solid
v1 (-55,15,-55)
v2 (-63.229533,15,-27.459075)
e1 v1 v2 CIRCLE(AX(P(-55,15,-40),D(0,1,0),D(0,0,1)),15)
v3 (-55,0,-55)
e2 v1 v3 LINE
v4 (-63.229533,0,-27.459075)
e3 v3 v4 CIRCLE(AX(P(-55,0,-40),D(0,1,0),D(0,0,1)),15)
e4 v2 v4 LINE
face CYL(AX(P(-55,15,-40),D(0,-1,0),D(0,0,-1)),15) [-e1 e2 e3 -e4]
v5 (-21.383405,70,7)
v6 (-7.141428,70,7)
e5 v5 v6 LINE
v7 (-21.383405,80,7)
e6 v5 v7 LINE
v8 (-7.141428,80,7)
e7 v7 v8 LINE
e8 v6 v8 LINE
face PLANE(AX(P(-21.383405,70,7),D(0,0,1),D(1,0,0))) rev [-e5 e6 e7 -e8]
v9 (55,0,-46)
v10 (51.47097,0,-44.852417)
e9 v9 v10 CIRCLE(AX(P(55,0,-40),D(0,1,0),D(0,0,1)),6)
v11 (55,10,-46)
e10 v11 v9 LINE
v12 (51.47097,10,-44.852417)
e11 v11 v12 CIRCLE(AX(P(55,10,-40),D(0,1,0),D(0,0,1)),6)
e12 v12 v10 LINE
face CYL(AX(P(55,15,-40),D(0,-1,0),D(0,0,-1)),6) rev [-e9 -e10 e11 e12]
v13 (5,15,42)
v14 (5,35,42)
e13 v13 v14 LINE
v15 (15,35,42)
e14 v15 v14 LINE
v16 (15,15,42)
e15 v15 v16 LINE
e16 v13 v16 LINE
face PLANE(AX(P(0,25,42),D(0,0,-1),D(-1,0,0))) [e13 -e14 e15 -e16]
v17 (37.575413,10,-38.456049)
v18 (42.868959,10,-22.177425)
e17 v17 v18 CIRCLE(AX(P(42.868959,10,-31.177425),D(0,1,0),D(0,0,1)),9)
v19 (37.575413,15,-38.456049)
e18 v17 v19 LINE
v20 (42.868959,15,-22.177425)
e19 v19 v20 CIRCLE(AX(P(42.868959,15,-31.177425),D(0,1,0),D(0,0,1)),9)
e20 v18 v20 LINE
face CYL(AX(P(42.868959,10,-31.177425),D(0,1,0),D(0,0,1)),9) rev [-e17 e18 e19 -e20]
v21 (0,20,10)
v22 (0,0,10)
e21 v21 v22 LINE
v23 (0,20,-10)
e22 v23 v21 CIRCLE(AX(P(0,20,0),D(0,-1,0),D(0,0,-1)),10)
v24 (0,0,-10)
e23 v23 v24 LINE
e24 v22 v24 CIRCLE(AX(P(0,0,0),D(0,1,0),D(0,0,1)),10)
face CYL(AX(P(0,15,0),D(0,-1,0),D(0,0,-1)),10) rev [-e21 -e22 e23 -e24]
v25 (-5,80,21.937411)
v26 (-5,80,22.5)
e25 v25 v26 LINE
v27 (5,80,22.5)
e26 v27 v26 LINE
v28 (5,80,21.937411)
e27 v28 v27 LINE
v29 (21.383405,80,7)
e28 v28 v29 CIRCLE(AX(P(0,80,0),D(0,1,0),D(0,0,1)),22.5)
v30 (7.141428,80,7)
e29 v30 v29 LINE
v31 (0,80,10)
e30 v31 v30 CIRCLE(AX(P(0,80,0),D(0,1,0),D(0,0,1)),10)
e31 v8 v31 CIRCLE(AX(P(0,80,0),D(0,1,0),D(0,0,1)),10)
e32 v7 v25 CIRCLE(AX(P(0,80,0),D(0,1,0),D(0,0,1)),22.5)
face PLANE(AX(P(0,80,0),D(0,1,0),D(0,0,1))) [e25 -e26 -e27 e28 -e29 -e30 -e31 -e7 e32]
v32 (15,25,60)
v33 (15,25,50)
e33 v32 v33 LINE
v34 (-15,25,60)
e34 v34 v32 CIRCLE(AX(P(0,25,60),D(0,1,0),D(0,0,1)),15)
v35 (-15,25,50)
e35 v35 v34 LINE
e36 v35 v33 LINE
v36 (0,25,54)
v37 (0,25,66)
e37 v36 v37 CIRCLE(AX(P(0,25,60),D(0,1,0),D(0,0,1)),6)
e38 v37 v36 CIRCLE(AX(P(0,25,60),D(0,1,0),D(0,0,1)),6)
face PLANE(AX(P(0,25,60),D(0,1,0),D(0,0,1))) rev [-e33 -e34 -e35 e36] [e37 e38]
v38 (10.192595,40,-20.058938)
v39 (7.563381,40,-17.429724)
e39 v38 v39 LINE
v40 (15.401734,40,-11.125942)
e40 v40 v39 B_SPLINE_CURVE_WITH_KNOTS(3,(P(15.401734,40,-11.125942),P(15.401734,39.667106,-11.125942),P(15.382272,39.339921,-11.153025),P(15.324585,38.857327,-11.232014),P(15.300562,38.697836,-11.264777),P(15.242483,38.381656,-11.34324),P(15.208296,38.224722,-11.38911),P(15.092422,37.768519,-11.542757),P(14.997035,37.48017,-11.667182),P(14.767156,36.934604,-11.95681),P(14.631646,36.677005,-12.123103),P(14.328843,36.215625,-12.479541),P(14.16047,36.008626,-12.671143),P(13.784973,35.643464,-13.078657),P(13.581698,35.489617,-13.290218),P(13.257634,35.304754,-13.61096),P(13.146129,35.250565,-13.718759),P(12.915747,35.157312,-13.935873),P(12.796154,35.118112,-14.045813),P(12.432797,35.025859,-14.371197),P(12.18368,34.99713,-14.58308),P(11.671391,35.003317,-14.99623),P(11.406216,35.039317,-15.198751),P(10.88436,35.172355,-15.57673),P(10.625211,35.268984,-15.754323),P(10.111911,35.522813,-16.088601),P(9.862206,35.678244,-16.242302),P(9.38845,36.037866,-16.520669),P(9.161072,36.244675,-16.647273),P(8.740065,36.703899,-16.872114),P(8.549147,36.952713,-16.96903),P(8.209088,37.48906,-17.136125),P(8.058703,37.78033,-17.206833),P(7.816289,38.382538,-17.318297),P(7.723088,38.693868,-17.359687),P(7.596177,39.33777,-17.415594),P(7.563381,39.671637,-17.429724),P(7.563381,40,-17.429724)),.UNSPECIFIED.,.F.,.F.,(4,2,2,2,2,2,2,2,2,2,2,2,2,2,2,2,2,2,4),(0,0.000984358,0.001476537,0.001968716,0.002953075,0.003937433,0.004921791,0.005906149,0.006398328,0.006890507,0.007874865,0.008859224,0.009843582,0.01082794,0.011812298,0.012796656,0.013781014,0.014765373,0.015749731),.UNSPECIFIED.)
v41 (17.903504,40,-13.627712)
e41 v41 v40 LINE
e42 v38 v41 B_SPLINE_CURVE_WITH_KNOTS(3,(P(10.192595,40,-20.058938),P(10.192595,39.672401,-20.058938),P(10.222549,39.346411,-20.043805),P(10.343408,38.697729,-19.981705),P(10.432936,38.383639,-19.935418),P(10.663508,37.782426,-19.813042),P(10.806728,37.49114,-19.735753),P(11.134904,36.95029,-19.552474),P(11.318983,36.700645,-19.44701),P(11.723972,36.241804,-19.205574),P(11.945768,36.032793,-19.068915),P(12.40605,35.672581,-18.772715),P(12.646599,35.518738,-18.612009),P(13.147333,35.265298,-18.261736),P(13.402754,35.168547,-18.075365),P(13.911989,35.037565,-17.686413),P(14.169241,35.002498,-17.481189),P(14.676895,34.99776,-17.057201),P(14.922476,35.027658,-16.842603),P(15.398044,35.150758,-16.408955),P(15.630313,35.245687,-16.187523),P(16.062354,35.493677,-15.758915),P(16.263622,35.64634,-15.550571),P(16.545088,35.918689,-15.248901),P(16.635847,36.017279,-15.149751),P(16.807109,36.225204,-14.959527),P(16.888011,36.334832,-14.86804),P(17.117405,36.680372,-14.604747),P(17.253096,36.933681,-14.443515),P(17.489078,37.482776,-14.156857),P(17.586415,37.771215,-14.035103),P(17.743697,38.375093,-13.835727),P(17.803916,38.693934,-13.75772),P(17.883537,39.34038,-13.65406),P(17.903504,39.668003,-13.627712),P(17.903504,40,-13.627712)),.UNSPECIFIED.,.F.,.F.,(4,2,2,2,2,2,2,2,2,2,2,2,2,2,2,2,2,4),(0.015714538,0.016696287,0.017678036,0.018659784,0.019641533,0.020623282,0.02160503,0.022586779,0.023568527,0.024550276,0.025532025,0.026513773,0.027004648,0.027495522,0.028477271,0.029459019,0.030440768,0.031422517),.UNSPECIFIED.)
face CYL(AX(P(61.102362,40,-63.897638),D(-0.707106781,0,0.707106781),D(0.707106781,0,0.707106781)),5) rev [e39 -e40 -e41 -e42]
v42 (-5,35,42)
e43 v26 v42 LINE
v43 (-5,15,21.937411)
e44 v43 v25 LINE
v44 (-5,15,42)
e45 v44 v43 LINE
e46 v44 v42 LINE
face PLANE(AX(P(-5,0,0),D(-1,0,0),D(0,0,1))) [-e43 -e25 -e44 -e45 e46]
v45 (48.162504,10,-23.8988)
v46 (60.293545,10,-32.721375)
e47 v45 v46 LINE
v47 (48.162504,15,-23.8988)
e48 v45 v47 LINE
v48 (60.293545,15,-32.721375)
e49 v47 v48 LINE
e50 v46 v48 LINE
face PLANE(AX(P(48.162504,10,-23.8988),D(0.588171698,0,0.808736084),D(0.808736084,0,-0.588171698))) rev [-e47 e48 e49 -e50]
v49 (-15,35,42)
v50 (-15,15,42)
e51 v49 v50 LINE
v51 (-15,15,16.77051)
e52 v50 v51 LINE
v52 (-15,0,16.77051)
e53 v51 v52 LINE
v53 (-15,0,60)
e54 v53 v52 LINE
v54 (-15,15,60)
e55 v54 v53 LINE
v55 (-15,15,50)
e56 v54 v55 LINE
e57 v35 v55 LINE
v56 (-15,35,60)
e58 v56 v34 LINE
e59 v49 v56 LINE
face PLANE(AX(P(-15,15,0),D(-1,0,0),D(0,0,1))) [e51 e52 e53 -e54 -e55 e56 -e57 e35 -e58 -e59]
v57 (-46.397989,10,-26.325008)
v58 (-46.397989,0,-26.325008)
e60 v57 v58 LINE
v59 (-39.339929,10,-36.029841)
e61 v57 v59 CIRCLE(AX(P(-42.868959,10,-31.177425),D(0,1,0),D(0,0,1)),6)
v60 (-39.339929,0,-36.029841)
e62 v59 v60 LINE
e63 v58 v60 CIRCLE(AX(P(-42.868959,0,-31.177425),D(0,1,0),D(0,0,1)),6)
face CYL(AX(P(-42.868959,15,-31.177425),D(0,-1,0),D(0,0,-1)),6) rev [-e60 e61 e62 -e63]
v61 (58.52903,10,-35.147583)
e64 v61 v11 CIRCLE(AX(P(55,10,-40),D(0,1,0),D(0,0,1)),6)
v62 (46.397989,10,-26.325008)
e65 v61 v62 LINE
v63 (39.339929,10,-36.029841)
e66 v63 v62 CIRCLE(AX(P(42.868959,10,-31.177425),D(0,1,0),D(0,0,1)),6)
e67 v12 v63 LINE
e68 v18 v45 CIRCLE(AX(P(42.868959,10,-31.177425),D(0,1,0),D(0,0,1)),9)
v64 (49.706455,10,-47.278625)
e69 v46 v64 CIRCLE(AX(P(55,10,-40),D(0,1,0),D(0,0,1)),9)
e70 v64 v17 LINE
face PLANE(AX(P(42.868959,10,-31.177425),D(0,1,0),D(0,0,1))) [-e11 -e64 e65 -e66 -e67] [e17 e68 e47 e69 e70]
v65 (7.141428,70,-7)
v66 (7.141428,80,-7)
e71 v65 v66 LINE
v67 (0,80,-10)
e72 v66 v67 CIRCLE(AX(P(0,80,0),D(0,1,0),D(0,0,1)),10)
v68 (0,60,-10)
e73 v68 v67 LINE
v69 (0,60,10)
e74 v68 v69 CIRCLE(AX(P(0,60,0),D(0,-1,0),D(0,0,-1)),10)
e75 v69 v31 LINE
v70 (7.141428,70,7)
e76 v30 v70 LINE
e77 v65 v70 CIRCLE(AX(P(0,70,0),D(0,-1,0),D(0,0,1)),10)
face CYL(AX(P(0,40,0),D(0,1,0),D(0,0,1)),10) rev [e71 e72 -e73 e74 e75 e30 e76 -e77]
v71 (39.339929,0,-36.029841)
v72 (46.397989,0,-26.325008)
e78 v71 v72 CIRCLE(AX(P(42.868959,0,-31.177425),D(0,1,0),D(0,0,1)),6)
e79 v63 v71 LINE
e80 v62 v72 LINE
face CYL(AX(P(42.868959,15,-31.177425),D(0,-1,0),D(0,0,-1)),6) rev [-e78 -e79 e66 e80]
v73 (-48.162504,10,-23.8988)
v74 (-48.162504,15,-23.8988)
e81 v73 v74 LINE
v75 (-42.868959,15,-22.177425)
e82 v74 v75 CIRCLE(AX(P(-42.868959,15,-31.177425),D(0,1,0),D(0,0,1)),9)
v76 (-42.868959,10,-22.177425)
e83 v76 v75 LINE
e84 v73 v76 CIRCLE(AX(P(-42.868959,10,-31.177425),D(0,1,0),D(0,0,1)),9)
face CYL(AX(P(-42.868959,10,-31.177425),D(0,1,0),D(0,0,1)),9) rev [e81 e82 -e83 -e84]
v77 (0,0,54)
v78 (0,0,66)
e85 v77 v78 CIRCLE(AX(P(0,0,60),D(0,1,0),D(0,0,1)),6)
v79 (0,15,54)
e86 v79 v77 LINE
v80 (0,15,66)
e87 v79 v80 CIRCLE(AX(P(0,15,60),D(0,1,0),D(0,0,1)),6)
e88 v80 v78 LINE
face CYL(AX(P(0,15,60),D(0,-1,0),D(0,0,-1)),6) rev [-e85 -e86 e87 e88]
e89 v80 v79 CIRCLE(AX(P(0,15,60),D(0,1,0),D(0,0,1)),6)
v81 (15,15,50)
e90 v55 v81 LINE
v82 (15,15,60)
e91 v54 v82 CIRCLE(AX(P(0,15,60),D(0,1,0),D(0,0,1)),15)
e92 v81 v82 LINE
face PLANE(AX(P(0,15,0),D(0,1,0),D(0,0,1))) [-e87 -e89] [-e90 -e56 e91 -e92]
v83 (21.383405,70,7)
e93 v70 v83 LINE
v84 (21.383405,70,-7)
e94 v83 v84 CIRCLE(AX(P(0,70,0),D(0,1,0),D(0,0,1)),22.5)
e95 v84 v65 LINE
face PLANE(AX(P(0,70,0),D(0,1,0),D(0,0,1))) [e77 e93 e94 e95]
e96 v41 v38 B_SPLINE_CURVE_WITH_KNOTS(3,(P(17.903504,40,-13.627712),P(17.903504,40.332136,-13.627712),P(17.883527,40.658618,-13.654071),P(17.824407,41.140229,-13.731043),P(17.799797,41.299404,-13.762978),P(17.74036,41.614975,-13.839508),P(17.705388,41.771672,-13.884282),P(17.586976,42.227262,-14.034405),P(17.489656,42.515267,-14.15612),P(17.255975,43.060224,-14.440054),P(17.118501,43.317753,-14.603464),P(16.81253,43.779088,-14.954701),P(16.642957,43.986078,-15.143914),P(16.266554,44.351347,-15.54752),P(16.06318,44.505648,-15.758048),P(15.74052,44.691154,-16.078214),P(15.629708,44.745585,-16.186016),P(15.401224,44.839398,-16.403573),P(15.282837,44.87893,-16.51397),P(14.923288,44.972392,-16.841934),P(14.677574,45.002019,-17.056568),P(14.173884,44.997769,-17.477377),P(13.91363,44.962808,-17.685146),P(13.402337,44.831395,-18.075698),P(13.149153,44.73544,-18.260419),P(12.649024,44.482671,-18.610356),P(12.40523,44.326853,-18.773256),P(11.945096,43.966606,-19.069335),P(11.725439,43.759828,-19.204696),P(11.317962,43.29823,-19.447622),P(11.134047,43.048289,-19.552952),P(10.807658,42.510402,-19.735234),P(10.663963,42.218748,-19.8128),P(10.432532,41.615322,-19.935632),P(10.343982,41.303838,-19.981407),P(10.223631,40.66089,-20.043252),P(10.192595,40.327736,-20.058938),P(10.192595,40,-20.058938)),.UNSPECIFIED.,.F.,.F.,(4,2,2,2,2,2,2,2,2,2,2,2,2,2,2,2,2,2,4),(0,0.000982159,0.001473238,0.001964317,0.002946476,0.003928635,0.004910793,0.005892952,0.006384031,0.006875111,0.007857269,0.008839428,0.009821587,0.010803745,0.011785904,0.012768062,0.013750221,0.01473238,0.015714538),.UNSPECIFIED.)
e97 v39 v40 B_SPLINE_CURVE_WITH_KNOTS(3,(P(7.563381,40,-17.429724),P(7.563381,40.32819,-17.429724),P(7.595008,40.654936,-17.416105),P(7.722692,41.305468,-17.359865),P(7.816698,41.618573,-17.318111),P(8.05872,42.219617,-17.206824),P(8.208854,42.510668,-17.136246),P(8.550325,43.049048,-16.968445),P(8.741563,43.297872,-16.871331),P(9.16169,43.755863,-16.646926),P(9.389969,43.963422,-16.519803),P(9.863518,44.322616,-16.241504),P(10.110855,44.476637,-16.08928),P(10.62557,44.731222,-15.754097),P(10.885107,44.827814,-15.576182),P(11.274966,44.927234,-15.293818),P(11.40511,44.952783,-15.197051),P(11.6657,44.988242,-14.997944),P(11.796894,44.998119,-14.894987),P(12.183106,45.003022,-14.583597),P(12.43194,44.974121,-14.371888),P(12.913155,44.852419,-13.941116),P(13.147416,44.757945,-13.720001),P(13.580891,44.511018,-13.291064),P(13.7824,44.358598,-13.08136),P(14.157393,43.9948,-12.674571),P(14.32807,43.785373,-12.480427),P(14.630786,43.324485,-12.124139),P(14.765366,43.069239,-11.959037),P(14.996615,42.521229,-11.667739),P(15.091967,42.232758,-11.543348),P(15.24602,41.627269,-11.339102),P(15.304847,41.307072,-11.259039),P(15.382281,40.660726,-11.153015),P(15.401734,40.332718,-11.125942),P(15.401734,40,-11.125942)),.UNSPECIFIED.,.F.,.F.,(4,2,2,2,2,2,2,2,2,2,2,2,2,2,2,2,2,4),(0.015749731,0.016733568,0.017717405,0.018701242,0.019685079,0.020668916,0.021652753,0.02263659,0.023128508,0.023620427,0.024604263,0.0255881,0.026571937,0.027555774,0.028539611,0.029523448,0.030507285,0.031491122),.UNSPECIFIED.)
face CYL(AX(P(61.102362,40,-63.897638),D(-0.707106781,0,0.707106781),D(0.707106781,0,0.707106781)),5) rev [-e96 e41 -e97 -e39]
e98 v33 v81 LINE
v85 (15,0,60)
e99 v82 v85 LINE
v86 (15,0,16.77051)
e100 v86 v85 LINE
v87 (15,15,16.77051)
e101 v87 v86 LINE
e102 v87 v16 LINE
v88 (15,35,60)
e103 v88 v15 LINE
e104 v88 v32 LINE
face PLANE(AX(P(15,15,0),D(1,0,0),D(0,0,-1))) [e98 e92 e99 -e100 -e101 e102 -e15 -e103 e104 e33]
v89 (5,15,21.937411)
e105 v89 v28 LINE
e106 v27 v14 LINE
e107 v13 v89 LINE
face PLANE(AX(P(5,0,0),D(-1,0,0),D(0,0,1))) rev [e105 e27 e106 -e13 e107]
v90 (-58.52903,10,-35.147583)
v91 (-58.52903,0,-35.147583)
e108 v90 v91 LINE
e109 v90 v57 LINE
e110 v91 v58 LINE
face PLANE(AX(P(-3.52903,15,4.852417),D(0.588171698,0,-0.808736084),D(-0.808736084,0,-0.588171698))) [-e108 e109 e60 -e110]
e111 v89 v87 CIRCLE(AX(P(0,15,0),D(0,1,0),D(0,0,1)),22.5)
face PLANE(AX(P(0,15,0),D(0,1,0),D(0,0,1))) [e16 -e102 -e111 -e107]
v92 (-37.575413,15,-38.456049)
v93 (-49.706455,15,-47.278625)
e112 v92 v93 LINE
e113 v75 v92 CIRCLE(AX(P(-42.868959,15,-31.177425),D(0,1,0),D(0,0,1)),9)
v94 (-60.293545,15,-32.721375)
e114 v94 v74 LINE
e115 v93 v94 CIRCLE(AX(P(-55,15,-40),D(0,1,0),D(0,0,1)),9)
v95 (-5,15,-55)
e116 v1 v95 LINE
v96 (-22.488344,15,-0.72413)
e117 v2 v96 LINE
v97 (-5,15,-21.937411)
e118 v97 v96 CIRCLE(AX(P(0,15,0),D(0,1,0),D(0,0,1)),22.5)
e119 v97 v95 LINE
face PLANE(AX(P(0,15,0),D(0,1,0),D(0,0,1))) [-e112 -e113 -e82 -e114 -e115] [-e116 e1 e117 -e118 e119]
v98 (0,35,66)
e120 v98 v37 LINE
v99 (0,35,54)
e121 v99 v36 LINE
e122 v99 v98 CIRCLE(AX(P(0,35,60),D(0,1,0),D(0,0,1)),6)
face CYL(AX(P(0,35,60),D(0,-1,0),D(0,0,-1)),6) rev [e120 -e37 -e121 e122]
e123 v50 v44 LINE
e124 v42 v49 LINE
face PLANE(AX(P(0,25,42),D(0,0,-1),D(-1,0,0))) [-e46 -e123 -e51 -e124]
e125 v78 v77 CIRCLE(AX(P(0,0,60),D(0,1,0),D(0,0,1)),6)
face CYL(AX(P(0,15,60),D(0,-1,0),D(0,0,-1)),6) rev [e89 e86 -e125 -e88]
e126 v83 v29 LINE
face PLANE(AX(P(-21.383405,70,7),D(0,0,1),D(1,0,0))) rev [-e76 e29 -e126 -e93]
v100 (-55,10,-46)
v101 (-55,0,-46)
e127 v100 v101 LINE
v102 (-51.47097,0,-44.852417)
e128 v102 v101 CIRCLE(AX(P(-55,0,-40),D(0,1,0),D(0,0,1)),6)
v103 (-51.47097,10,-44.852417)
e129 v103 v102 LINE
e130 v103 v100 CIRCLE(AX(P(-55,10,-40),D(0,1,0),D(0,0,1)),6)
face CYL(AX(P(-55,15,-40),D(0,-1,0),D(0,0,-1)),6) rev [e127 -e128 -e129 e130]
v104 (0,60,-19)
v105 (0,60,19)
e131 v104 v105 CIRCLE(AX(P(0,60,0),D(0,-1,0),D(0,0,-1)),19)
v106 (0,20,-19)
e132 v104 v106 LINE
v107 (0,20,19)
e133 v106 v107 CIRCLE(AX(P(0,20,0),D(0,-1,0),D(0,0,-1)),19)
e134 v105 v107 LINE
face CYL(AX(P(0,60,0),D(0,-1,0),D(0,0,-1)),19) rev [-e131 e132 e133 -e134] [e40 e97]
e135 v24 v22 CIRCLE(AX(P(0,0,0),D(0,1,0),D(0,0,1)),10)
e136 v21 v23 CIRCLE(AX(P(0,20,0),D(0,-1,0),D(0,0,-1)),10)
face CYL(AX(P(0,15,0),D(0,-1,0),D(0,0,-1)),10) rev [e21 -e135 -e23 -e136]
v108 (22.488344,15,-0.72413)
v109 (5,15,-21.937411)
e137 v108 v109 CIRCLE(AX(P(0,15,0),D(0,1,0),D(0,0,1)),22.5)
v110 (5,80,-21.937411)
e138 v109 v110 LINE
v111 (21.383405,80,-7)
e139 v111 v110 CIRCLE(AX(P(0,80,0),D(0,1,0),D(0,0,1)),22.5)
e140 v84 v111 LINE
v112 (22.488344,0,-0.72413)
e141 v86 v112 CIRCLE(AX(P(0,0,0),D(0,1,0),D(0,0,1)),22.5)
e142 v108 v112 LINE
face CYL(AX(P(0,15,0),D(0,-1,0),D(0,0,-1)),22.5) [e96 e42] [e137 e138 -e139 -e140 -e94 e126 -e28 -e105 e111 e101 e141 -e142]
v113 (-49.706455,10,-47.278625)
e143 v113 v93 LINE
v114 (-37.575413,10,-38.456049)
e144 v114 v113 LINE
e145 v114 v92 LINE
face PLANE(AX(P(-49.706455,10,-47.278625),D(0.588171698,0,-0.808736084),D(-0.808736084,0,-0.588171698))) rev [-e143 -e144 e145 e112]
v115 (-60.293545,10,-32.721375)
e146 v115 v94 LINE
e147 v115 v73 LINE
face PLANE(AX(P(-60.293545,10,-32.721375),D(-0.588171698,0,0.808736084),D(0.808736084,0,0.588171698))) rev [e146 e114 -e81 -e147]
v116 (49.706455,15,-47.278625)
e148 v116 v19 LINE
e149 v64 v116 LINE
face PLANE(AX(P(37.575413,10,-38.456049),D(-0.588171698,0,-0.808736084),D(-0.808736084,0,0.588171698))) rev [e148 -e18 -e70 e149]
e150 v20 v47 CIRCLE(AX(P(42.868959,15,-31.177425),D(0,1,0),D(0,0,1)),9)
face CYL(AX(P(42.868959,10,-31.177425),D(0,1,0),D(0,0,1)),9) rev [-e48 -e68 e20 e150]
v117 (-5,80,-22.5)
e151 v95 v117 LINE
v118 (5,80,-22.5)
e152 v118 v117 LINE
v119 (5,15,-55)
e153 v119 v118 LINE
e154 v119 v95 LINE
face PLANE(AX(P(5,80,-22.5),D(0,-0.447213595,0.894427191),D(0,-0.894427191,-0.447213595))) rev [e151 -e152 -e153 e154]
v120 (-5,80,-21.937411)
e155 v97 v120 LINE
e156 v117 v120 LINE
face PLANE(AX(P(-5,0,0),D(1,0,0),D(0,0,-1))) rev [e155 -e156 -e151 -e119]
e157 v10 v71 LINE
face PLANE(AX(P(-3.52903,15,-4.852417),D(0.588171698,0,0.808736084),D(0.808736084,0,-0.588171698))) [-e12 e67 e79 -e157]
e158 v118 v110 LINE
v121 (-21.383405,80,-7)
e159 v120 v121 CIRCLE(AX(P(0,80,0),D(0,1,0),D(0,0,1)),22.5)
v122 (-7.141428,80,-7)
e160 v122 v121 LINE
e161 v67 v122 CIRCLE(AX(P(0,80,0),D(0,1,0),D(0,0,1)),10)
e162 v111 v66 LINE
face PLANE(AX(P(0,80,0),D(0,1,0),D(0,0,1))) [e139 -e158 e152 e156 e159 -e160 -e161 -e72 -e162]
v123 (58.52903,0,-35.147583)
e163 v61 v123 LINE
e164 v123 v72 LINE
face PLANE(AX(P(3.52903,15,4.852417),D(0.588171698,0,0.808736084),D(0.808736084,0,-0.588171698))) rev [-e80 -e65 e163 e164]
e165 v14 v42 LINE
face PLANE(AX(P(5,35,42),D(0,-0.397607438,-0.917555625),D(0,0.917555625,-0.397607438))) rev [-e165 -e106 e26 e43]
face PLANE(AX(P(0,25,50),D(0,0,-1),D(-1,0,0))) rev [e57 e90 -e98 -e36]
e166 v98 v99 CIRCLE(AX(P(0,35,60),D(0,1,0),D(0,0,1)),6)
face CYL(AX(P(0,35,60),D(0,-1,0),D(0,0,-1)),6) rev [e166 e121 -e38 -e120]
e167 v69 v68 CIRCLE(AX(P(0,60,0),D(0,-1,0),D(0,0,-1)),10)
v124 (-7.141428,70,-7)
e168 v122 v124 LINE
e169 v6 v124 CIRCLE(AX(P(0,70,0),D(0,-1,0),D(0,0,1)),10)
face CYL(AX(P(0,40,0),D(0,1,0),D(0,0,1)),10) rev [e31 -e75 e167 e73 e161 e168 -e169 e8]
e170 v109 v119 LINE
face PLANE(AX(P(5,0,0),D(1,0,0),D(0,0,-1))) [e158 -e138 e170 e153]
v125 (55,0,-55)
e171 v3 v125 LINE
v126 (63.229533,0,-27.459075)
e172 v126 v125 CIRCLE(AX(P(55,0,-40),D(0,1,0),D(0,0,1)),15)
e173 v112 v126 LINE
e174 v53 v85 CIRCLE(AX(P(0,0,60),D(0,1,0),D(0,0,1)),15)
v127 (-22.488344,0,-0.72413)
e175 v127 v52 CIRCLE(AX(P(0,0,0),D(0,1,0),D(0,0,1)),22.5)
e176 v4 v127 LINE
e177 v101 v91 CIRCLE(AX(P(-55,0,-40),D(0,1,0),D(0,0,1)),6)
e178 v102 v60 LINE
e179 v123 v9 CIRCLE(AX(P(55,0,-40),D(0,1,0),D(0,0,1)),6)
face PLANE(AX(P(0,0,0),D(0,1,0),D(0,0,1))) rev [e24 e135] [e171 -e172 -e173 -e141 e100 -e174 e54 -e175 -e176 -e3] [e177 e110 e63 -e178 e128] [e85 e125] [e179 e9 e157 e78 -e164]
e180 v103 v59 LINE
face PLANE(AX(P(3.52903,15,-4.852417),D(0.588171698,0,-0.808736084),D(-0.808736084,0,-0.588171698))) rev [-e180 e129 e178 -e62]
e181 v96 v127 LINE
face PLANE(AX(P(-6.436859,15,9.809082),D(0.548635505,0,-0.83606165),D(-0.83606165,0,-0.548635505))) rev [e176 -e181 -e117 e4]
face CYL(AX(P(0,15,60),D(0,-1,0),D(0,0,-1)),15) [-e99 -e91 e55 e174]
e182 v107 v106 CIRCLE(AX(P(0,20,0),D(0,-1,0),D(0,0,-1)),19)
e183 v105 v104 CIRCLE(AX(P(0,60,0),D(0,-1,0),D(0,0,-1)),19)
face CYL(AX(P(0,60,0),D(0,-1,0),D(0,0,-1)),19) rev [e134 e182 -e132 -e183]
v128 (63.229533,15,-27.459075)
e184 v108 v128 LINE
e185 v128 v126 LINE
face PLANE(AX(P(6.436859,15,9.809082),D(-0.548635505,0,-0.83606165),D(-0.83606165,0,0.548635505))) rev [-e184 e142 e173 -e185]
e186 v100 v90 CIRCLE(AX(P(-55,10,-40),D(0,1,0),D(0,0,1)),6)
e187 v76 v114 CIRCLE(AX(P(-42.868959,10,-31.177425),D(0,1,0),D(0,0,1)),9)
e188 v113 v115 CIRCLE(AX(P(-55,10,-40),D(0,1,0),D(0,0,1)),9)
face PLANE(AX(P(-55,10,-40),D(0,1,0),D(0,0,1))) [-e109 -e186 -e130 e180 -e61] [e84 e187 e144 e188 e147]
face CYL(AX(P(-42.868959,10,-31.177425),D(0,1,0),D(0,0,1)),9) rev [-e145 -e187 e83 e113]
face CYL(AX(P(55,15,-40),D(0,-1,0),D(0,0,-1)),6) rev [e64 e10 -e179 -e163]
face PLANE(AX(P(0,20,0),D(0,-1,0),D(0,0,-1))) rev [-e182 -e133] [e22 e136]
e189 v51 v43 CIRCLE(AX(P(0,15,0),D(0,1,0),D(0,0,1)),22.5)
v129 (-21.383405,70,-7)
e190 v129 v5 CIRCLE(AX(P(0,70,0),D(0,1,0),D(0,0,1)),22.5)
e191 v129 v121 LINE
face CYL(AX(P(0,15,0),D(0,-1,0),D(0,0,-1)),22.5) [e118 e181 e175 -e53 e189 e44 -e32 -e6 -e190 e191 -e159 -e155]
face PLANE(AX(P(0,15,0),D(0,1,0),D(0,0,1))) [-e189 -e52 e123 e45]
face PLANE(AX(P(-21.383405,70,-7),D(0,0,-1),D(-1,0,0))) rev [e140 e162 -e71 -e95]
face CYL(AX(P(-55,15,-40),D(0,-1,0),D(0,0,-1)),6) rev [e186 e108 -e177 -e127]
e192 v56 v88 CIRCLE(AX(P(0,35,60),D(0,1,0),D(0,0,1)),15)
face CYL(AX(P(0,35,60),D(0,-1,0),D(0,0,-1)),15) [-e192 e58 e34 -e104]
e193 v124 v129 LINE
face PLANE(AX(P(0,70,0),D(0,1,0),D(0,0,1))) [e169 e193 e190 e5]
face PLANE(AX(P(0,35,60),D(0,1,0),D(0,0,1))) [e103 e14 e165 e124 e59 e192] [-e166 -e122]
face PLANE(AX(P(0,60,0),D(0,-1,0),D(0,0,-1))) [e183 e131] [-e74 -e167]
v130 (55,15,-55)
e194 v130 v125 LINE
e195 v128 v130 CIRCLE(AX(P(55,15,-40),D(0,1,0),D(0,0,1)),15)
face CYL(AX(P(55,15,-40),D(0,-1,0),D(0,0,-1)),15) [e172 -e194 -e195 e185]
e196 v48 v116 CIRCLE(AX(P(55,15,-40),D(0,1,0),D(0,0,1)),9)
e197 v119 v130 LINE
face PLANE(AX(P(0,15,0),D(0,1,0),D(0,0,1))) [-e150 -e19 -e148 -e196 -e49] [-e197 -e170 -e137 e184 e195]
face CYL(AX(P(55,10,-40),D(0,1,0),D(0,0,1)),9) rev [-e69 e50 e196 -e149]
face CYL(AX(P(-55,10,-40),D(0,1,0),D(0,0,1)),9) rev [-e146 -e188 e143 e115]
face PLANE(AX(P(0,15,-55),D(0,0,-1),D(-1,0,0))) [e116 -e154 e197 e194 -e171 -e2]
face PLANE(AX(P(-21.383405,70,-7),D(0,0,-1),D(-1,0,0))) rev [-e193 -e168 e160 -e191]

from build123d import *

# Parameters (mm, degrees)
TRI_ARM_BASE_PROFILE_R         = 22.5
TRI_ARM_BASE_PROFILE_R_2       = 10
TRI_ARM_BASE_PROFILE_R_3       = 6
TRI_ARM_BASE_PLATE_DEPTH       = 15
ARM_POCKET_DEPTH               = 5
CLEVIS_LUG_PROFILE_W           = 30
CLEVIS_LUG_PROFILE_H           = 8
CLEVIS_LUG_DEPTH               = 10
CLEVIS_LUG_EXTENSION_PROFILE_R = 6
CLEVIS_LUG_EXTENSION_DEPTH     = 10
TRUNNION_HUB_PROFILE_45_R      = 22.5
TRUNNION_HUB_45_DEPTH          = 65
HUB_ENTRY_BORE_PROFILE_20_R    = 10
HUB_ENTRY_BORE_20_DEPTH        = 5
HUB_BORE_PROFILE_38_R          = 19
HUB_BORE_38_DEPTH              = 40
HUB_START                      = -40
HUB_THROUGH_BORE_PROFILE_20_R  = 10
HUB_THROUGH_BORE_20_DEPTH      = 40
HUB_START_2                    = -10
HUB_TOP_SLOT_14MM_DEPTH        = 10
GUSSET_RIB_DEPTH               = 5
CLEVIS_PIN_HOLE_PROFILE_10_R   = 5
CLEVIS_PIN_HOLE_10_DEPTH       = 131.096118313


with BuildPart() as part:
    # Tri-Arm Base Profile → Tri-Arm Base Plate (new body)
    # profile 1 of 3: a face of its own
    with BuildSketch(Plane(origin=(0, 0, 0), x_dir=(1, 0, 0), z_dir=(0, 1, 0))):
        with BuildLine():
            Line((55, 55), (-55, 55))
            ThreePointArc((-55, 55), (-69.372088771, 44.294538898), (-63.22953257, 27.459075246))
            Line((-63.22953257, 27.459075246), (-22.488344437, 0.724130156))
            ThreePointArc((-22.488344437, 0.724130156), (0, 22.5), (22.488344437, 0.724130156))
            Line((22.488344437, 0.724130156), (63.22953257, 27.459075246))
            ThreePointArc((63.22953257, 27.459075246), (69.372088771, 44.294538898), (55, 55))
        make_face()
        with BuildLine():
            ThreePointArc((-58.529030186, 35.147583494), (-59.852416506, 43.529030186), (-51.470969814, 44.852416506))
            Line((-51.470969814, 44.852416506), (-39.339928549, 36.029841041))
            ThreePointArc((-39.339928549, 36.029841041), (-38.01654223, 27.648394349), (-46.397988922, 26.325008029))
            Line((-46.397988922, 26.325008029), (-58.529030186, 35.147583494))
        make_face(mode=Mode.SUBTRACT)
        with BuildLine():
            ThreePointArc((51.470969814, 44.852416506), (59.852416506, 43.529030186), (58.529030186, 35.147583494))
            Line((58.529030186, 35.147583494), (46.397988922, 26.325008029))
            ThreePointArc((46.397988922, 26.325008029), (38.01654223, 27.648394349), (39.339928549, 36.029841041))
            Line((39.339928549, 36.029841041), (51.470969814, 44.852416506))
        make_face(mode=Mode.SUBTRACT)
    # profile 2 of 3: a face of its own
    with BuildSketch(Plane(origin=(0, 0, 0), x_dir=(1, 0, 0), z_dir=(0, 1, 0))):
        Circle(TRI_ARM_BASE_PROFILE_R)
        with Locations(Location((0, 0, 0), (0, 0, 270))):
            Circle(TRI_ARM_BASE_PROFILE_R_2, mode=Mode.SUBTRACT)
    # profile 3 of 3: a face of its own
    with BuildSketch(Plane(origin=(0, 0, 0), x_dir=(1, 0, 0), z_dir=(0, 1, 0))):
        with BuildLine():
            ThreePointArc((15, -16.770509831), (0, -22.5), (-15, -16.770509831))
            Line((-15, -16.770509831), (-15, -60))
            ThreePointArc((-15, -60), (0, -75), (15, -60))
            Line((15, -60), (15, -16.770509831))
        make_face()
        with Locations(Location((0, -60, 0), (0, 0, 270))):
            Circle(TRI_ARM_BASE_PROFILE_R_3, mode=Mode.SUBTRACT)
    extrude(amount=TRI_ARM_BASE_PLATE_DEPTH)

    # Arm Pocket Profile → Arm Pocket (cut)
    with BuildSketch(Plane(origin=(0, 15, 0), x_dir=(1, 0, 0), z_dir=(0, 1, 0))):
        with BuildLine():
            Line((-49.706454721, 47.278624759), (-37.575413456, 38.456049294))
            ThreePointArc((-37.575413456, 38.456049294), (-35.590333977, 25.883879256), (-48.162504015, 23.898799776))
            Line((-48.162504015, 23.898799776), (-60.293545279, 32.721375241))
            ThreePointArc((-60.293545279, 32.721375241), (-62.278624759, 45.293545279), (-49.706454721, 47.278624759))
        make_face()
        with BuildLine():
            Line((37.575413456, 38.456049294), (49.706454721, 47.278624759))
            ThreePointArc((49.706454721, 47.278624759), (62.278624759, 45.293545279), (60.293545279, 32.721375241))
            Line((60.293545279, 32.721375241), (48.162504015, 23.898799776))
            ThreePointArc((48.162504015, 23.898799776), (35.590333977, 25.883879256), (37.575413456, 38.456049294))
        make_face()
    extrude(amount=-ARM_POCKET_DEPTH, mode=Mode.SUBTRACT)

    # Clevis Lug Profile → Clevis Lug (add)
    with BuildSketch(Plane(origin=(0, 15, 0), x_dir=(1, 0, 0), z_dir=(0, 1, 0))):
        with Locations((0, -46)):
            Rectangle(CLEVIS_LUG_PROFILE_W, CLEVIS_LUG_PROFILE_H)
    extrude(amount=CLEVIS_LUG_DEPTH)

    # Clevis Lug Extension Profile → Clevis Lug Extension (add)
    with BuildSketch(Plane(origin=(0, 25, 0), x_dir=(1, 0, 0), z_dir=(0, 1, 0))):
        with BuildLine():
            Line((-15, -42), (-15, -60))
            ThreePointArc((-15, -60), (0, -75), (15, -60))
            Line((15, -60), (15, -42))
            Line((15, -42), (-15, -42))
        make_face()
        with Locations(Location((0, -60, 0), (0, 0, 270))):
            Circle(CLEVIS_LUG_EXTENSION_PROFILE_R, mode=Mode.SUBTRACT)
    extrude(amount=CLEVIS_LUG_EXTENSION_DEPTH)

    # Trunnion Hub Profile Ø45 → Trunnion Hub Ø45 (add)
    with BuildSketch(Plane(origin=(0, 15, 0), x_dir=(1, 0, 0), z_dir=(0, 1, 0))):
        with Locations(Location((0, 0, 0), (0, 0, 1.844300776))):
            Circle(TRUNNION_HUB_PROFILE_45_R)
    extrude(amount=TRUNNION_HUB_45_DEPTH)

    # Hub Entry Bore Profile Ø20 → Hub Entry Bore Ø20 (cut)
    with BuildSketch(Plane.XZ.offset(-15)):
        with Locations(Location((0, 0, 0), (0, 0, 270))):
            Circle(HUB_ENTRY_BORE_PROFILE_20_R)
    extrude(amount=-HUB_ENTRY_BORE_20_DEPTH, mode=Mode.SUBTRACT)

    # Hub Bore Profile Ø38 → Hub Bore Ø38 (cut)
    with BuildSketch(Plane.XZ.offset(-20)):
        with Locations(Location((0, 0, 0), (0, 0, 270))):
            Circle(HUB_BORE_PROFILE_38_R)
    extrude(amount=-HUB_BORE_38_DEPTH, mode=Mode.SUBTRACT)

    # Hub Through Bore Profile Ø20 → Hub Through Bore Ø20 (cut)
    with BuildSketch(Plane(origin=(0, 80, 0), x_dir=(1, 0, 0), z_dir=(0, 1, 0)).offset(HUB_START)):
        with Locations(Location((0, 0, 0), (0, 0, 90))):
            Circle(HUB_THROUGH_BORE_PROFILE_20_R)
    extrude(amount=HUB_THROUGH_BORE_20_DEPTH, mode=Mode.SUBTRACT)

    # Hub Top Slot Profile → Hub Top Slot 14mm (cut)
    with BuildSketch(Plane(origin=(0, 80, 0), x_dir=(1, 0, 0), z_dir=(0, 1, 0)).offset(HUB_START_2)):
        with BuildLine():
            Line((-21.38340478, -7), (21.38340478, -7))
            ThreePointArc((21.38340478, -7), (22.5, 0), (21.38340478, 7))
            Line((21.38340478, 7), (-21.38340478, 7))
            ThreePointArc((-21.38340478, 7), (-22.5, 0), (-21.38340478, -7))
        make_face()
    extrude(amount=HUB_TOP_SLOT_14MM_DEPTH, mode=Mode.SUBTRACT)

    # Gusset Rib Profile → Gusset Rib (add, symmetric)
    with BuildSketch(Plane(origin=(0, 0, 0), x_dir=(0, 0, -1), z_dir=(1, 0, 0))):
        Polygon((-42, 35), (-22.5, 80), (-19.5, 80), (-19.5, 15), (-44.156903801, 15), (-44.156903801, 35), align=None)
        Polygon((22.5, 80), (55, 15), (20.047322275, 15), (20.047322275, 80), align=None)
    extrude(amount=GUSSET_RIB_DEPTH, both=True)

    # Clevis Pin Hole Profile Ø10 → Clevis Pin Hole Ø10 (cut, through all)
    with BuildSketch(Plane(origin=(0, 0, 0), x_dir=(0.7071067811865477, 0, 0.7071067811865475), z_dir=(-0.7071067811865475, 0, 0.7071067811865477))):
        with Locations((-1.976558152, 40)):
            Circle(CLEVIS_PIN_HOLE_PROFILE_10_R)
    extrude(amount=-CLEVIS_PIN_HOLE_10_DEPTH, mode=Mode.SUBTRACT)


solid = part.part
